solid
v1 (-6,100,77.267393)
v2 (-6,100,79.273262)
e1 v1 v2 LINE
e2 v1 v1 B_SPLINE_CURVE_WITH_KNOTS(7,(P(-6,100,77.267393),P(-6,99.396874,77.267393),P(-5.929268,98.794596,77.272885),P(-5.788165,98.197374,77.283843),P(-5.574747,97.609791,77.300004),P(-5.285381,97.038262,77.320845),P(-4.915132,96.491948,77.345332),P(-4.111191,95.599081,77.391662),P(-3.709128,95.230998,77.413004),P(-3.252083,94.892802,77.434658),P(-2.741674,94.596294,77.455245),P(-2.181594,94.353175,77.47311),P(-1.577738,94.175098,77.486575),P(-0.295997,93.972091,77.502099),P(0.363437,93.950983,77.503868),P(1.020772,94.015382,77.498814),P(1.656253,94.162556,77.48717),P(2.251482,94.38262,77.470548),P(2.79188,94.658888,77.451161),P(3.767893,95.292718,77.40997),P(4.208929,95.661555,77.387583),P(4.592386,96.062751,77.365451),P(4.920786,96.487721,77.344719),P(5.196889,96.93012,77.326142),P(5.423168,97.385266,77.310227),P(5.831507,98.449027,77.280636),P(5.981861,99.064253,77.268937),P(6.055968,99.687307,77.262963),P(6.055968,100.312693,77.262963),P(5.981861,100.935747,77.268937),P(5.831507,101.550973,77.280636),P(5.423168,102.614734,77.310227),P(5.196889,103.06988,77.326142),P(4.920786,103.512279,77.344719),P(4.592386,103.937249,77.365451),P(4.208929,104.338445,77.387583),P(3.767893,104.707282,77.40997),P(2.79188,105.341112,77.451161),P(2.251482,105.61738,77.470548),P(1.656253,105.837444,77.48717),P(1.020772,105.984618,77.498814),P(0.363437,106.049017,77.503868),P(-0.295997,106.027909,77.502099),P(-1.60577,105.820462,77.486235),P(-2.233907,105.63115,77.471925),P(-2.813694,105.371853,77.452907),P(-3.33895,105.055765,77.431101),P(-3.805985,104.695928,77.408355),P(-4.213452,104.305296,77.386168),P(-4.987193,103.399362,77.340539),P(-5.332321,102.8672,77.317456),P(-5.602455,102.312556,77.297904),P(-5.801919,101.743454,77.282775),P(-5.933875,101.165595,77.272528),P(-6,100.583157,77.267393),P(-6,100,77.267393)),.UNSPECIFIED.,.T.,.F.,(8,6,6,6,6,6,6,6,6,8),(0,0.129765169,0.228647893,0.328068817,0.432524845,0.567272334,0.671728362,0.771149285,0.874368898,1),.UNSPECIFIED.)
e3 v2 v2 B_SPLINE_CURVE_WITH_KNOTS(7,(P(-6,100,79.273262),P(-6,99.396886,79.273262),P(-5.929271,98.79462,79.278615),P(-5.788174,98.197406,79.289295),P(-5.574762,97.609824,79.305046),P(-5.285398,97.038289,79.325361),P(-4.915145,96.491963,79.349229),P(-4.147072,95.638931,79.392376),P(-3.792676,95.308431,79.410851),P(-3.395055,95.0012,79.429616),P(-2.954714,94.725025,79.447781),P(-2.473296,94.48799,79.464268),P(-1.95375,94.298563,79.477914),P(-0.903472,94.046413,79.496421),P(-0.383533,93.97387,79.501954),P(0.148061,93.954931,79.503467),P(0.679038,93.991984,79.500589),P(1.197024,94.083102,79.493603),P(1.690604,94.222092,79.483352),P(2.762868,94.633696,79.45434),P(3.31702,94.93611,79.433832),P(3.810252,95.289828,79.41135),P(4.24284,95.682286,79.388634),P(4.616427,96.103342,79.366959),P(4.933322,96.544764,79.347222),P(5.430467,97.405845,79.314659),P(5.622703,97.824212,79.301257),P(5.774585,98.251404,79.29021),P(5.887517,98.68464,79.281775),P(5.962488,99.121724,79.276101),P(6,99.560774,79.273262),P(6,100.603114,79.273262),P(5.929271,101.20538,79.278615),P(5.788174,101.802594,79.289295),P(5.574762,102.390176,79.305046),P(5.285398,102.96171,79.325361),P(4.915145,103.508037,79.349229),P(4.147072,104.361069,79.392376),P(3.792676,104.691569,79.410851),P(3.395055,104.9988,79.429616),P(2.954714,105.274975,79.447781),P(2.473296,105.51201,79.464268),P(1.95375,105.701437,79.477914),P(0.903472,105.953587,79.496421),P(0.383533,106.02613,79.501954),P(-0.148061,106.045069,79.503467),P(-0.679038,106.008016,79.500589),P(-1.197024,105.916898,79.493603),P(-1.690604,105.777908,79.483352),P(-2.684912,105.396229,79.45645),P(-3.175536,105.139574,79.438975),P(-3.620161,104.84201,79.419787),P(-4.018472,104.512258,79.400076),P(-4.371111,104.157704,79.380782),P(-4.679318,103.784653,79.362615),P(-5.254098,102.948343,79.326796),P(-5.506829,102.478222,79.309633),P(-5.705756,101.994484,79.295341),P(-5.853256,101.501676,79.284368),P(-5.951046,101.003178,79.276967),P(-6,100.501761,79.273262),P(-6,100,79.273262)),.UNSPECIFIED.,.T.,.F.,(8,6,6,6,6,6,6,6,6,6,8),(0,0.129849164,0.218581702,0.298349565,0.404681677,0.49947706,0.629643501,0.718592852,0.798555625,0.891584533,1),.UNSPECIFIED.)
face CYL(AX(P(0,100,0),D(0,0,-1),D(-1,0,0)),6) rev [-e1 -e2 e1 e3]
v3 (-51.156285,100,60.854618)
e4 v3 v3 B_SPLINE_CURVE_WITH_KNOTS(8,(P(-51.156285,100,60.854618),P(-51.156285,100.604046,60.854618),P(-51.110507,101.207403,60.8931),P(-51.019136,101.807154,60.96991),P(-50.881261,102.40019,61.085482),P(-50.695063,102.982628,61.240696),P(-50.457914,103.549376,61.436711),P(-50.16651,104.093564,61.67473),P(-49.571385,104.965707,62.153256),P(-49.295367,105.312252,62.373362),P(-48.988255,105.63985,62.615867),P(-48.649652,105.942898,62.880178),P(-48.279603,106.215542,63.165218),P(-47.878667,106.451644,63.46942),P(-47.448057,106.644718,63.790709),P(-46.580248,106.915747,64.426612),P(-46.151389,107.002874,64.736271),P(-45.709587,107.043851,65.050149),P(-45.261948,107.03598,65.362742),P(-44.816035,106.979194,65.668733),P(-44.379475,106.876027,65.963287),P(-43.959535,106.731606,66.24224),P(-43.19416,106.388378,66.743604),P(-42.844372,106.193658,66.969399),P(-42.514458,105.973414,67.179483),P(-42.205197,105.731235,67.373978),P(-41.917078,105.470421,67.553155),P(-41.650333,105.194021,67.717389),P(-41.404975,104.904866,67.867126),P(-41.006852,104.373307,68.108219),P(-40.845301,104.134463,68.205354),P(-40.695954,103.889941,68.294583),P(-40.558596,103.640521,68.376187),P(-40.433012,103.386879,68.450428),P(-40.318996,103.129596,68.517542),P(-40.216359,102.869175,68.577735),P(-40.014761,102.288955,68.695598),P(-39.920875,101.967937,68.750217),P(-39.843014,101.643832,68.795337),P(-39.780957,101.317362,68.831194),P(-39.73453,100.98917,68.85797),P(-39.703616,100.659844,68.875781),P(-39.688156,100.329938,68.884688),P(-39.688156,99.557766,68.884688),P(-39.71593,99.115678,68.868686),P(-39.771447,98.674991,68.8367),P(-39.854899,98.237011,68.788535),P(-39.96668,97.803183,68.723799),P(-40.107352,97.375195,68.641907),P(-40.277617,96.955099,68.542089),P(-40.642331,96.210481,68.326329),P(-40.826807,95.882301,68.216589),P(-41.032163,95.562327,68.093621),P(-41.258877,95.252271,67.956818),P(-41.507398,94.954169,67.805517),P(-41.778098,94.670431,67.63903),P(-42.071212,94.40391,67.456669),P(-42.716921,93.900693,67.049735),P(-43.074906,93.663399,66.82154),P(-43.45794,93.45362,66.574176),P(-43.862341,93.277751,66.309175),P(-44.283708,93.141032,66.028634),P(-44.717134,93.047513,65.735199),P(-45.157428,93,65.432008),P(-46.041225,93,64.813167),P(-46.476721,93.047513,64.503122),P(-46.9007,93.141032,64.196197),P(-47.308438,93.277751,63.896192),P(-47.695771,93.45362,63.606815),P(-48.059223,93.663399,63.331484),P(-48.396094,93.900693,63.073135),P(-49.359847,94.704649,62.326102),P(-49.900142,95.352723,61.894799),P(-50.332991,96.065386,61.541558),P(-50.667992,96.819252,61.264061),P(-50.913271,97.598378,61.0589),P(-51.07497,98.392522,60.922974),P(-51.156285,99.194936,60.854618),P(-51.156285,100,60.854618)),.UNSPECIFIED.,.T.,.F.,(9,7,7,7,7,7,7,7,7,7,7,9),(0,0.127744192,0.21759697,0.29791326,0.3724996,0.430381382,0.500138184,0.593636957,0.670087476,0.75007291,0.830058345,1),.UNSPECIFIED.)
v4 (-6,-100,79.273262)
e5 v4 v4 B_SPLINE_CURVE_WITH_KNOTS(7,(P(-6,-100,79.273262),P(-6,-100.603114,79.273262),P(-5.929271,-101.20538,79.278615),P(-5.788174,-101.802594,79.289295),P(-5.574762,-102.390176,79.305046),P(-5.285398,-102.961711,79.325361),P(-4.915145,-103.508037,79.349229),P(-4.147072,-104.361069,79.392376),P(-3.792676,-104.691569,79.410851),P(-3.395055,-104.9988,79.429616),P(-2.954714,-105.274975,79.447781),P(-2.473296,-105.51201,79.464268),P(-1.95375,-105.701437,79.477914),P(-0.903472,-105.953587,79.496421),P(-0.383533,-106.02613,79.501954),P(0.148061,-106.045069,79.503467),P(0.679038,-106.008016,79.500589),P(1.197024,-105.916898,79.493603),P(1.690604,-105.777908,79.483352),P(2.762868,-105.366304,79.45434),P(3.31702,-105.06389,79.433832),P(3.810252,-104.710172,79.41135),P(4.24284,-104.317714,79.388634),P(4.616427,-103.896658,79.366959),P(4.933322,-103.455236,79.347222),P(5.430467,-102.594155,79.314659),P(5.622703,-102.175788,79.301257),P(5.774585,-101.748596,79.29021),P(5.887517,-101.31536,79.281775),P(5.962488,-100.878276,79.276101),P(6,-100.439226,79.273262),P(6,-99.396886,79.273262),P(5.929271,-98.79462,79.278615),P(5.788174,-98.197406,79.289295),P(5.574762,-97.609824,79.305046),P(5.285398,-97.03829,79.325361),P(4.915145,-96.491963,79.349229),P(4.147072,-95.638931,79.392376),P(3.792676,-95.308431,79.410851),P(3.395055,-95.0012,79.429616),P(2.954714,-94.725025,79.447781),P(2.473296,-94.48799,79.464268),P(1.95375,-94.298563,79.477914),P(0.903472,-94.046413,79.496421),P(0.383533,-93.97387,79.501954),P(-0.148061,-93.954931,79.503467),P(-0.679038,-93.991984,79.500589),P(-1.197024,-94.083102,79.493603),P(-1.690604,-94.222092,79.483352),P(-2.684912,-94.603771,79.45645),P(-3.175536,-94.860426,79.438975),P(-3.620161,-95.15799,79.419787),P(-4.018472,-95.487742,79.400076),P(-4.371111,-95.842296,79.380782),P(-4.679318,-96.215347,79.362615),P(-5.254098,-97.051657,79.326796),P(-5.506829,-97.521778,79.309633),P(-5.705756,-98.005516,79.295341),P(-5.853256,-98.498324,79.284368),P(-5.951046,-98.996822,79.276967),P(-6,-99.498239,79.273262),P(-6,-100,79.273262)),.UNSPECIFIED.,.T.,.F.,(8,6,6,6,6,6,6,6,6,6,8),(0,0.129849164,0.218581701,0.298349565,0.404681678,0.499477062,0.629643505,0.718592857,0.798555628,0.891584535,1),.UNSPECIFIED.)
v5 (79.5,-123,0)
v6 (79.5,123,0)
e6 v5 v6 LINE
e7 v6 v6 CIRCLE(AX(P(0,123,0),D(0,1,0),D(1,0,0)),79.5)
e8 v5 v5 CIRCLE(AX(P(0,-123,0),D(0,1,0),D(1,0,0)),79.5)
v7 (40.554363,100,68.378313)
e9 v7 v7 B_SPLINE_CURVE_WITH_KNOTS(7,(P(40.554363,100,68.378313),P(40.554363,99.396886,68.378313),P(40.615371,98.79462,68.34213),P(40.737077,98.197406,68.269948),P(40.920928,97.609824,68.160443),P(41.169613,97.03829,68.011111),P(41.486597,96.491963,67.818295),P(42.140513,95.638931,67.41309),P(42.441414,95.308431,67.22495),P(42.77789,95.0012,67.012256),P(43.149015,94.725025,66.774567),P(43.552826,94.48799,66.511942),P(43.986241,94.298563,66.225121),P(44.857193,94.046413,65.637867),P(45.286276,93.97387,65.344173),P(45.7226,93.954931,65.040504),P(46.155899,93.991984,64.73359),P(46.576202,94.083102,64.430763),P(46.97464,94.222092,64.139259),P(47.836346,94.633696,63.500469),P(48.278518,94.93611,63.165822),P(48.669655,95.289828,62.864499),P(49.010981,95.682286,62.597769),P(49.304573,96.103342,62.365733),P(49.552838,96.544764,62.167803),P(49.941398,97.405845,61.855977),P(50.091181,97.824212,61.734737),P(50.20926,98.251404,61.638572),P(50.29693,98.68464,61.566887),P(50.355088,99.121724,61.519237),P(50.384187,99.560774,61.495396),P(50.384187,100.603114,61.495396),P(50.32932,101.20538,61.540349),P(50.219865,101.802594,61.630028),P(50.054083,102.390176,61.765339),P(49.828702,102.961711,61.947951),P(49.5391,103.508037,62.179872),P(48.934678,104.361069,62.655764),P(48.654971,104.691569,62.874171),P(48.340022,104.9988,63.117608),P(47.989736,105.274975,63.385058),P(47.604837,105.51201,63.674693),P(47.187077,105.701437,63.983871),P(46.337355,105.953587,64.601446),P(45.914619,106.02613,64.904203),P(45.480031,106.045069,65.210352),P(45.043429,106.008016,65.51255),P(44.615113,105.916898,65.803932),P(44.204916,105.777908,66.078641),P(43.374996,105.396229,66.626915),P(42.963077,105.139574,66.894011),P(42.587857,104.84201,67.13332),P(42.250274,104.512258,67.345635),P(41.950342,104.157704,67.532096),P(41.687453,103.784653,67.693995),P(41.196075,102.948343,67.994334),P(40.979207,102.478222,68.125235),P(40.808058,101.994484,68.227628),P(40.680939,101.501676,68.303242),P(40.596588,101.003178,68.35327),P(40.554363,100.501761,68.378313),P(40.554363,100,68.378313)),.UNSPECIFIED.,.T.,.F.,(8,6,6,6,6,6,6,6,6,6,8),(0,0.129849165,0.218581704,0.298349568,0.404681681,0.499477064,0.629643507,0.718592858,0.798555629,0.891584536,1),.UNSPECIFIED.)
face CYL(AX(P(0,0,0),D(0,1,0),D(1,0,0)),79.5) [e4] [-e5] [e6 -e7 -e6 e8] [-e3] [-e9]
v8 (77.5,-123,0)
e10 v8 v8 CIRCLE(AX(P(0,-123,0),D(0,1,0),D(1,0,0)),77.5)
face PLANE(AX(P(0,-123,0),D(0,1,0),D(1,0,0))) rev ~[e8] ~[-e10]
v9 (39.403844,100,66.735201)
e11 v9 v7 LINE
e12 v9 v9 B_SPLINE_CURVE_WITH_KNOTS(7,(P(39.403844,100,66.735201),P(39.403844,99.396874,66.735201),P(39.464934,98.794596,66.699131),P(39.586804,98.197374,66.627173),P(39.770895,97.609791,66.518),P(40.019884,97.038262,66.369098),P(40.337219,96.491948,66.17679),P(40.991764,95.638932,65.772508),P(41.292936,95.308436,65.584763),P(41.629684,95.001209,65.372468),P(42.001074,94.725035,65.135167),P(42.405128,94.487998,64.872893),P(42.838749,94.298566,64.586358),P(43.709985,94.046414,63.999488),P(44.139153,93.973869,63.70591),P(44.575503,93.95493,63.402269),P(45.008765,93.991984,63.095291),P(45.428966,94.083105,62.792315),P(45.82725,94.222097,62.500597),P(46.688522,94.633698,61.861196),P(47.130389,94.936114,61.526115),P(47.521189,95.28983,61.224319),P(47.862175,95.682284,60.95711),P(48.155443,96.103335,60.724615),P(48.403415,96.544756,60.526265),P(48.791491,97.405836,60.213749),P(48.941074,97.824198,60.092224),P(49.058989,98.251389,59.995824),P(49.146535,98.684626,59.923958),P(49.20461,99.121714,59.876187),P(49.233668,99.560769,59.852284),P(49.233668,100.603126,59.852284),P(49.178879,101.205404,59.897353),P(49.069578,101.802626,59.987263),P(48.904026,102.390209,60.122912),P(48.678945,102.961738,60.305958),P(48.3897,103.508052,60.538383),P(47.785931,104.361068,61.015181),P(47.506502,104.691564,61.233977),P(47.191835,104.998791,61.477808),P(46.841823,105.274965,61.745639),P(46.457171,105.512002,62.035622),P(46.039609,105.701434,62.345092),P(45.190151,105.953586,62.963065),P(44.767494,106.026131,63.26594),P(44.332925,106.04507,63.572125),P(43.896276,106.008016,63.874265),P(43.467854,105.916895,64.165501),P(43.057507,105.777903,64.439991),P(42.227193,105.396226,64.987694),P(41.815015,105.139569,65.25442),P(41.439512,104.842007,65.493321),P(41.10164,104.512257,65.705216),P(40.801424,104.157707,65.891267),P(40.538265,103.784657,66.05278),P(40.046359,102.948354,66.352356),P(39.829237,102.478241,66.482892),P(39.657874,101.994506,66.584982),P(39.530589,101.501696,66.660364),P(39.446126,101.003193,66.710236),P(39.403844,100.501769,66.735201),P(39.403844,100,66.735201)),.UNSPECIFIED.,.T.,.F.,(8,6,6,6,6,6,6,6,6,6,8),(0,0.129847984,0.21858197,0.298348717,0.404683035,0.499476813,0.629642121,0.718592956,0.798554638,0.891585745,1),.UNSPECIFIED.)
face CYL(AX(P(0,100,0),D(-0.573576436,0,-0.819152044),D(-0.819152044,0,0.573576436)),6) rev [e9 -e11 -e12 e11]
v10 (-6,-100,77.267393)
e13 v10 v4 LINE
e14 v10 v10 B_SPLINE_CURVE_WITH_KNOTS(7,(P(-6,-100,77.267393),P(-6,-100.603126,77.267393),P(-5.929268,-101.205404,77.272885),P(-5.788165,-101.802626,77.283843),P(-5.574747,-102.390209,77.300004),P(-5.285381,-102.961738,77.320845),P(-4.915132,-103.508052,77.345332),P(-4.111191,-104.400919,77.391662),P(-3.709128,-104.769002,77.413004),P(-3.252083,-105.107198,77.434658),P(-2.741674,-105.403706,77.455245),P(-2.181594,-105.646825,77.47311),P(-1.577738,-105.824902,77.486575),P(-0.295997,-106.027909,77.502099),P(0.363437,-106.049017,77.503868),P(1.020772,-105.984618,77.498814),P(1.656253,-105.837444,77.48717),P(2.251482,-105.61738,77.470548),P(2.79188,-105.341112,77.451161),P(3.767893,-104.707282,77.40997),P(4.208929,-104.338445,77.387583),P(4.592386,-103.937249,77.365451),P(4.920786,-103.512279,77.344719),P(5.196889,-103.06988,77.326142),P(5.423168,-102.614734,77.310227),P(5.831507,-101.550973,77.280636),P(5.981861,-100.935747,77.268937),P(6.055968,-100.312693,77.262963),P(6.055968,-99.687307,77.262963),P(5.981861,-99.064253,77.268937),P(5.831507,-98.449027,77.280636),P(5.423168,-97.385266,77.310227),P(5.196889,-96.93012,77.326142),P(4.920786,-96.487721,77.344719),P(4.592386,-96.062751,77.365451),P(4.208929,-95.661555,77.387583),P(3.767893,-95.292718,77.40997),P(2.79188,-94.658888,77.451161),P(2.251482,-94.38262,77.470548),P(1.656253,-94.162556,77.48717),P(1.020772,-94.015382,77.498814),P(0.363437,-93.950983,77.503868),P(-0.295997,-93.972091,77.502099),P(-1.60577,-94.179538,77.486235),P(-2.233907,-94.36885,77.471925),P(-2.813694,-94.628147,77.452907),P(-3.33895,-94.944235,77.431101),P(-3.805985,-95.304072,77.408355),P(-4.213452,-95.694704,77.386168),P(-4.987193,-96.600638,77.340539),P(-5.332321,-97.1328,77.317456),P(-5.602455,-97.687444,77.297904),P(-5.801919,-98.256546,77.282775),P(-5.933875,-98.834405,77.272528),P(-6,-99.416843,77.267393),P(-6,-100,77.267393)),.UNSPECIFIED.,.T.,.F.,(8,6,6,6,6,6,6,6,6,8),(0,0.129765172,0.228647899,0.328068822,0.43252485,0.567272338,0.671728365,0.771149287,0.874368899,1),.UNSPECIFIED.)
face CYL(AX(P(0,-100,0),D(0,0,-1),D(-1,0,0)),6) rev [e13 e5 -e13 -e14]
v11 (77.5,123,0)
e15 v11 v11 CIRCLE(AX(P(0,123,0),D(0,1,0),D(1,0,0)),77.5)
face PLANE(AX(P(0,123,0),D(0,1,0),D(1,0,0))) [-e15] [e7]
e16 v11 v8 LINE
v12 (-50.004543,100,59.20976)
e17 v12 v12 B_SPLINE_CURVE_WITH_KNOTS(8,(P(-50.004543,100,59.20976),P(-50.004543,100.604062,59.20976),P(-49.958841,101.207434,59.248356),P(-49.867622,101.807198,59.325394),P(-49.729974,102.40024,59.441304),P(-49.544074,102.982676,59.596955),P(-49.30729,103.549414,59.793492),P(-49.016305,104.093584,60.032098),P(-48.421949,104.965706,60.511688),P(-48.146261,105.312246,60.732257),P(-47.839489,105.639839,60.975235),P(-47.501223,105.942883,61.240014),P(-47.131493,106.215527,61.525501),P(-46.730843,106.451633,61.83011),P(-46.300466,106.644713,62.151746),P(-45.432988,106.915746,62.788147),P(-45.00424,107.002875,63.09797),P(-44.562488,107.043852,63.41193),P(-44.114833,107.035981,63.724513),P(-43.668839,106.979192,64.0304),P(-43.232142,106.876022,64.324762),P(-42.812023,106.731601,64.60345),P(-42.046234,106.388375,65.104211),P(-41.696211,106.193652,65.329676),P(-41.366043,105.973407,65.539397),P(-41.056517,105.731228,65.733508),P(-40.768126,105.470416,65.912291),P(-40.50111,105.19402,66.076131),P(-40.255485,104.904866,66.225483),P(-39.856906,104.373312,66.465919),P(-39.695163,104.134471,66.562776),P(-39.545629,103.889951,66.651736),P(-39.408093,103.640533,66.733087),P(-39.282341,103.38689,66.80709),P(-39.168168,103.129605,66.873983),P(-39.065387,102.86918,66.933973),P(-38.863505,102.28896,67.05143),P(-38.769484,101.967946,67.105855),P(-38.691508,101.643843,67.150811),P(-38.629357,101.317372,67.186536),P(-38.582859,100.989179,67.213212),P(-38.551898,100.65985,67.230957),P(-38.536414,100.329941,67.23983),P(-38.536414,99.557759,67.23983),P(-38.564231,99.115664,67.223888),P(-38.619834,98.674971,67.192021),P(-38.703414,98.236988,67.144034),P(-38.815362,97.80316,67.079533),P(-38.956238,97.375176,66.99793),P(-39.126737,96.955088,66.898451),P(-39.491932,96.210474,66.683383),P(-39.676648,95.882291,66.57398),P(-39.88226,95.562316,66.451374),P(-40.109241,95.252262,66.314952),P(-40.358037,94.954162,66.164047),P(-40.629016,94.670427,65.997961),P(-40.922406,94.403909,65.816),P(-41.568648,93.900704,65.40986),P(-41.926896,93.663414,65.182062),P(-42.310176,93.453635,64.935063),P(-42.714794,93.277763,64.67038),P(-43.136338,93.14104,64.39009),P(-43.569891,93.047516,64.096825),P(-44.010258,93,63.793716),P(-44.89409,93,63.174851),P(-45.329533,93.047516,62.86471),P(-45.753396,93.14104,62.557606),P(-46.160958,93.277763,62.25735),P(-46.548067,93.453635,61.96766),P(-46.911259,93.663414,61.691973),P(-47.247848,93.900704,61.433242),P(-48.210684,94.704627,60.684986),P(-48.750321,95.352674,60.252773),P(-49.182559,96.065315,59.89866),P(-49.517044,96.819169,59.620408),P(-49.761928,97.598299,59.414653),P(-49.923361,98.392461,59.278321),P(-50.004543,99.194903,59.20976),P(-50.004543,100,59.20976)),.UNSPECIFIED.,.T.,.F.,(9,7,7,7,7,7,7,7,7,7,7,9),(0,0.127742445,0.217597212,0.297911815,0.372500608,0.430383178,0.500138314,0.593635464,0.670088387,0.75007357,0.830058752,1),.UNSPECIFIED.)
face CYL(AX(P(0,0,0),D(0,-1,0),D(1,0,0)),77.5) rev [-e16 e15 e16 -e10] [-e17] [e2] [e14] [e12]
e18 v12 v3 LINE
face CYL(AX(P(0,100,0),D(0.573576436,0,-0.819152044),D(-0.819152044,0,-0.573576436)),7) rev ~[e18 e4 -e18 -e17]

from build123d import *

# Parameters (mm, degrees)
SKETCH_2_R          = 79.5
SKETCH_2_R_2        = 77.5
EXTRUDE_1_DEPTH     = 123
SKETCH_3_R          = 6
CUT_EXTRUDE_2_DEPTH = 167.641831483
SKETCH_4_R          = 6
CUT_EXTRUDE_3_DEPTH = 167.641831653
SKETCH_5_R          = 7
CUT_EXTRUDE_4_DEPTH = 167.641831653


with BuildPart() as part:
    # 草图2 → 拉伸-薄壁1 (new, symmetric)
    with BuildSketch(Plane(origin=(0, 0, 0), x_dir=(1, 0, 0), z_dir=(0, 1, 0))):
        Circle(SKETCH_2_R)
        Circle(SKETCH_2_R_2, mode=Mode.SUBTRACT)
    extrude(amount=EXTRUDE_1_DEPTH, both=True)

    # 草图3 → 切除-拉伸2 (cut, through all)
    with BuildSketch(Plane.XY):
        with Locations(Location((0, 100, 0), (0, 0, 180))):
            Circle(SKETCH_3_R)
        with Locations(Location((0, -100, 0), (0, 0, 180))):
            Circle(SKETCH_3_R)
    extrude(amount=CUT_EXTRUDE_2_DEPTH, mode=Mode.SUBTRACT)

    # 草图4 → 切除-拉伸3 (cut, through all)
    with BuildSketch(Plane(origin=(0, 0, 0), x_dir=(0, -1, 0), z_dir=(0.5735764363510444, 0, 0.819152044288993))):
        with Locations(Location((-100, 0, 0), (0, 0, 270))):
            Circle(SKETCH_4_R)
    extrude(amount=CUT_EXTRUDE_3_DEPTH, mode=Mode.SUBTRACT)

    # 草图5 → 切除-拉伸4 (cut, through all)
    with BuildSketch(Plane(origin=(0, 0, 0), x_dir=(0, -1, 0), z_dir=(0.5735764363510444, 0, -0.819152044288993))):
        with Locations(Location((-100, 0, 0), (0, 0, 90))):
            Circle(SKETCH_5_R)
    extrude(amount=-CUT_EXTRUDE_4_DEPTH, mode=Mode.SUBTRACT)


solid = part.part
